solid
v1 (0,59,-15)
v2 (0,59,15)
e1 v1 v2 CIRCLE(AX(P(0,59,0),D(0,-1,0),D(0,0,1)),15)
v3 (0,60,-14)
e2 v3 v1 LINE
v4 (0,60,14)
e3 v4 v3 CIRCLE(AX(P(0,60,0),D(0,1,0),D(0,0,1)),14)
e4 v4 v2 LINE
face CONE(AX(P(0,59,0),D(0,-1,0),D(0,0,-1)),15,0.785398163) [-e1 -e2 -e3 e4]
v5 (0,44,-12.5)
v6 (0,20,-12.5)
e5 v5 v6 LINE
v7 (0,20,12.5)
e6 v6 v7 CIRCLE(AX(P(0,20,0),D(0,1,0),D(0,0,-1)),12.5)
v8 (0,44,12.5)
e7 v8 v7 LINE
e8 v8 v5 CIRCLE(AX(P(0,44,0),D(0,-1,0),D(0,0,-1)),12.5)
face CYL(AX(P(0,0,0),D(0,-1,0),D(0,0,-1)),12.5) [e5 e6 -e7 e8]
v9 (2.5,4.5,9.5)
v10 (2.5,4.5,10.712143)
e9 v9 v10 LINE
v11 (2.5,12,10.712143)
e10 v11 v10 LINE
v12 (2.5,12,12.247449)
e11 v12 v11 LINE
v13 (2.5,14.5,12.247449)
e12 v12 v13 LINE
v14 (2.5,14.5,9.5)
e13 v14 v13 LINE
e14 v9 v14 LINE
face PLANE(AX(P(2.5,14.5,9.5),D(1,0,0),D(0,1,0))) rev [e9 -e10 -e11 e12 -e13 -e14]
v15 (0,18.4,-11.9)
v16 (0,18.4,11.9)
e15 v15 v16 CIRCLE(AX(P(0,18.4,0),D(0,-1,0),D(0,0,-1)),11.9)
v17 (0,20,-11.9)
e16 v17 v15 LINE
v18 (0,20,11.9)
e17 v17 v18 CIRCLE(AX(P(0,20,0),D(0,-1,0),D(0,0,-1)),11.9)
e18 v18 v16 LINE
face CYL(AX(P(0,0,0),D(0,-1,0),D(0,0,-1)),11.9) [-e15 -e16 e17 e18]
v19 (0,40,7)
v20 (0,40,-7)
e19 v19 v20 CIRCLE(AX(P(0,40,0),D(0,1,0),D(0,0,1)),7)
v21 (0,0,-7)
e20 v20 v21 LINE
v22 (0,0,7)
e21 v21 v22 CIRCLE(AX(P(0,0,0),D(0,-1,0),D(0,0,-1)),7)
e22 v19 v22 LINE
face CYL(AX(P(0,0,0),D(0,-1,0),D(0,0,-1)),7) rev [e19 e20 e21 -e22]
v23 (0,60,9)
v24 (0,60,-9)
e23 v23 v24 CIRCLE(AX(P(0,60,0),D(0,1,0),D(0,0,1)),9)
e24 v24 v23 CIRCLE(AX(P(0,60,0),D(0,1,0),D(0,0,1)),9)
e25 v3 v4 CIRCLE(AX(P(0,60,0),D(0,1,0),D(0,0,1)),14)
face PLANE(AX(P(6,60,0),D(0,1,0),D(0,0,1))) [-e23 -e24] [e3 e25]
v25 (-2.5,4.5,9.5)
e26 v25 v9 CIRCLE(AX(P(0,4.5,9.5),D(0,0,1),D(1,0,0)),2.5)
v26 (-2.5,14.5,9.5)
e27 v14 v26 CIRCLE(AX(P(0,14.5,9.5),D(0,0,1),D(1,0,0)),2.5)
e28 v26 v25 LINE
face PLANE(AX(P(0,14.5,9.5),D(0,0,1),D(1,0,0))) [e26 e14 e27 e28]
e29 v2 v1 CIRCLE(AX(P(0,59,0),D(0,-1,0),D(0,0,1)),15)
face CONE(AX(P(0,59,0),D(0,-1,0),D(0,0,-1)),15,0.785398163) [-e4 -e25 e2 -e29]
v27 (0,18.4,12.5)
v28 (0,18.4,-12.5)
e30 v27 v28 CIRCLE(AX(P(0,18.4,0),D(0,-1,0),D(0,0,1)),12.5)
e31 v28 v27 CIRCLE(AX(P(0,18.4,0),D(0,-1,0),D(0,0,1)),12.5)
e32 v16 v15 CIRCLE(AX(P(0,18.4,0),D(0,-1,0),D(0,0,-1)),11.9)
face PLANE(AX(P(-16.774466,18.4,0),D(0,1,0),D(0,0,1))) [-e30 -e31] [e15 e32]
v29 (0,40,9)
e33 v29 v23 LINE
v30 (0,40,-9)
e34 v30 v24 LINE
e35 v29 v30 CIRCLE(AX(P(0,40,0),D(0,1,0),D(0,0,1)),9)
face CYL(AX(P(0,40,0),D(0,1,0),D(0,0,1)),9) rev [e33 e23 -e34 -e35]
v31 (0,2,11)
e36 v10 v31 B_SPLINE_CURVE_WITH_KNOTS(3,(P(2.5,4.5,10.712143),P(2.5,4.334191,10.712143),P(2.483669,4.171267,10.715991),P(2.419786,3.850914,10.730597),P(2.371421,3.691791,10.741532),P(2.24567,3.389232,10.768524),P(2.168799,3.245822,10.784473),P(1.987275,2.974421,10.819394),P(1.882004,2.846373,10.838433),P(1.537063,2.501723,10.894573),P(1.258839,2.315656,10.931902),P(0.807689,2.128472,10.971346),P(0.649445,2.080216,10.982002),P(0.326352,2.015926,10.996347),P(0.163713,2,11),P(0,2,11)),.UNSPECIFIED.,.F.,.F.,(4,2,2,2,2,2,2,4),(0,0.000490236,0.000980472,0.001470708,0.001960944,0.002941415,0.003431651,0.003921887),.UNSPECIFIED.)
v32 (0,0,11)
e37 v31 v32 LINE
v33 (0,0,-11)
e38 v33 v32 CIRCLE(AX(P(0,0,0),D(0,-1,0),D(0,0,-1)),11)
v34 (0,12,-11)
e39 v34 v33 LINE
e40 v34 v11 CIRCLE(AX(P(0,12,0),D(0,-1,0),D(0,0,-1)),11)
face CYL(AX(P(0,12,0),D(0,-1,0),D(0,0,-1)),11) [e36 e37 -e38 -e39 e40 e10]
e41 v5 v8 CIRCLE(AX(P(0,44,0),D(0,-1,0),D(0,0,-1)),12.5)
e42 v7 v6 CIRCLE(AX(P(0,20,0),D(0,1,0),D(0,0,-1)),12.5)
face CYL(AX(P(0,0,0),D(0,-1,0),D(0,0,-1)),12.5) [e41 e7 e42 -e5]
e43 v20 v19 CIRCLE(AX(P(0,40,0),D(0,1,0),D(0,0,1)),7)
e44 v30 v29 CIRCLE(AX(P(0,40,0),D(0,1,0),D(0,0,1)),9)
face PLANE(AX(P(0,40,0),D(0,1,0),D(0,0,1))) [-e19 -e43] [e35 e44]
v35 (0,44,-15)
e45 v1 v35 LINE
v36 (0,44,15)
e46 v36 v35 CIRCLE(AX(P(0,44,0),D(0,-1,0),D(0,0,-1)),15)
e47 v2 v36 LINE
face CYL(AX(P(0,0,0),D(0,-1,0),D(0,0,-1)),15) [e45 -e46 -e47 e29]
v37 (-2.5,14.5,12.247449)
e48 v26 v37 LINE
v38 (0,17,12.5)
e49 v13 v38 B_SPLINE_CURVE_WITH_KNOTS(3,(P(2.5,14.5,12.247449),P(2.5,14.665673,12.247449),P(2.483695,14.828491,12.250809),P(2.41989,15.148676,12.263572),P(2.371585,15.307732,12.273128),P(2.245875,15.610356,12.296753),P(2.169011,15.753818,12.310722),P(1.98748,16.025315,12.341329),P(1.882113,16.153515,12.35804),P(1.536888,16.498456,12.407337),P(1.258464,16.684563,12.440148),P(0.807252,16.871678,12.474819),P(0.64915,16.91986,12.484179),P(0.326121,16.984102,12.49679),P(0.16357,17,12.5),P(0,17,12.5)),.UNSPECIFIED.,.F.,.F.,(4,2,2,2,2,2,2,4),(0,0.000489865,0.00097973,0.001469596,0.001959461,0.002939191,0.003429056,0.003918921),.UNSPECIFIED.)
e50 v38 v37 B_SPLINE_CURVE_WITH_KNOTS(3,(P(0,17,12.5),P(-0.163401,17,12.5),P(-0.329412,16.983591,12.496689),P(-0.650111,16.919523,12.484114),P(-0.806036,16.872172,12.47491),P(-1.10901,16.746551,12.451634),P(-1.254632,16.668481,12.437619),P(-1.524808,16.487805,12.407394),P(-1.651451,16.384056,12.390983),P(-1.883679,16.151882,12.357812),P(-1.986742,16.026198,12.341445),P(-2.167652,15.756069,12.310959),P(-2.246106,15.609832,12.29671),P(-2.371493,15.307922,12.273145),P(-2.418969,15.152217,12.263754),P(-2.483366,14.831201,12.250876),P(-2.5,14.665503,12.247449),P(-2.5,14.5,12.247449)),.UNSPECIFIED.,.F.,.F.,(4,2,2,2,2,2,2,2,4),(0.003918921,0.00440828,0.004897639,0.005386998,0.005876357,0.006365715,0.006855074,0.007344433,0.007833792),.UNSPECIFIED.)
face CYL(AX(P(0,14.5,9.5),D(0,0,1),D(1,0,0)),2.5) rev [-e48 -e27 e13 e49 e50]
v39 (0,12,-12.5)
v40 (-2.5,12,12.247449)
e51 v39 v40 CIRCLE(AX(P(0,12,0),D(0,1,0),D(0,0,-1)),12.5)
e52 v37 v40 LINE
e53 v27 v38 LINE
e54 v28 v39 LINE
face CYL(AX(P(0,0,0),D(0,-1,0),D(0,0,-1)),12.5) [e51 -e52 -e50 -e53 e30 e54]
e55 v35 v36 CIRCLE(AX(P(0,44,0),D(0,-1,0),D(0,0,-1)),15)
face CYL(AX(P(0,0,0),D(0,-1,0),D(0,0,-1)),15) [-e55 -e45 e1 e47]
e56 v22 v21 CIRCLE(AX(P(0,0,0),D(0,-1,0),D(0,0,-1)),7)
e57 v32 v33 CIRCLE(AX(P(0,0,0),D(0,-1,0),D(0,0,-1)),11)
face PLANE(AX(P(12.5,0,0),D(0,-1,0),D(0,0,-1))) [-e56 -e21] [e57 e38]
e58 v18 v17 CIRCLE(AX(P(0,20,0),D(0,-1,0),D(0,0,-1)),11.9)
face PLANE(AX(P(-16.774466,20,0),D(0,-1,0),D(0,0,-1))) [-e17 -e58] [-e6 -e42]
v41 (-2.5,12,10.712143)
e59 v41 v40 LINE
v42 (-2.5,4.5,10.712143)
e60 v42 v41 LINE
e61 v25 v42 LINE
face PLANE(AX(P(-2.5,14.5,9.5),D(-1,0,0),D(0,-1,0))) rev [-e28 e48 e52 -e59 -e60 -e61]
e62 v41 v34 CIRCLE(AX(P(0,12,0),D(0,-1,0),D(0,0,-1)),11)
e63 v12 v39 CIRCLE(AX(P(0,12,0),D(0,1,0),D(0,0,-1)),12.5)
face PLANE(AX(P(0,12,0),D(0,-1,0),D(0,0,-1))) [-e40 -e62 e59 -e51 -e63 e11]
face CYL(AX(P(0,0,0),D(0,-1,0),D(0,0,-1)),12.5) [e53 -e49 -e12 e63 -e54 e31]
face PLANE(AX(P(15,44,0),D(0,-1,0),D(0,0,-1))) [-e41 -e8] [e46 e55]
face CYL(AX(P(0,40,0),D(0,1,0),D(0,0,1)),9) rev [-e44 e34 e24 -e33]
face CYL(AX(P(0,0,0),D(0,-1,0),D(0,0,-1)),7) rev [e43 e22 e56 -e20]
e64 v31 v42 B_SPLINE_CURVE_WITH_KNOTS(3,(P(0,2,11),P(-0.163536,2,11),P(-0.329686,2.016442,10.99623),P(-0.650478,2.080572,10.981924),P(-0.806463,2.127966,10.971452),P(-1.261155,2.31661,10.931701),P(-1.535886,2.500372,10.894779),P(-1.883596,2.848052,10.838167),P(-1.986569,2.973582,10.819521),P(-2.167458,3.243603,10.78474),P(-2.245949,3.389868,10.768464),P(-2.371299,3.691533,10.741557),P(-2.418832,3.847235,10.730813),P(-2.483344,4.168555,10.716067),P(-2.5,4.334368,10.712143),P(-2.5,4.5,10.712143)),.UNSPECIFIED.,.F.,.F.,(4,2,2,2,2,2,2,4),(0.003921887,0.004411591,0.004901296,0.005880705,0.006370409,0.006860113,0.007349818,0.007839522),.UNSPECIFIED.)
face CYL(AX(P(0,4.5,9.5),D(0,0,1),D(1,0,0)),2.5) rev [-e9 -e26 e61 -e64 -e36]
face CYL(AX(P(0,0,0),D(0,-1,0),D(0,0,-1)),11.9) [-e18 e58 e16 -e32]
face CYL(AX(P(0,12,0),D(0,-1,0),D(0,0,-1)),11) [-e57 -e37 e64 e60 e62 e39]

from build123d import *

# Parameters (mm, degrees)
SKETCH2_W          = 4.874466188
SKETCH2_H          = 1.6
SKETCH3_R          = 9
CUT_EXTRUDE1_DEPTH = 20
M16_TAPPED_HOLE2_D = 14
CHAMFER1_SIZE      = 1
CUT_EXTRUDE2_START = 12.5
CUT_EXTRUDE2_DEPTH = 3
SKETCH10_R         = 15
SKETCH10_R_2       = 11
CUT_EXTRUDE3_DEPTH = 12


with BuildPart() as part:
    # Sketch1 → Revolve1 (revolve)
    with BuildSketch(Plane.XY, mode=Mode.PRIVATE) as revolve1_sk:
        Polygon((6, 60), (15, 60), (15, 44), (12.5, 44), (12.5, 0), (6, 0), align=None)
    revolve(revolve1_sk.sketch.rotate(Axis((0, 0, 0), (0, 1, 0)), 90), axis=Axis((0, 0, 0), (0, 1, 0)))

    # Sketch2 → Cut-Revolve1 (revolve, cut)
    with BuildSketch(Plane.XY, mode=Mode.PRIVATE) as cut_revolve1_sk:
        with Locations((-14.337233094, 19.2)):
            Rectangle(SKETCH2_W, SKETCH2_H)
    revolve(cut_revolve1_sk.sketch.rotate(Axis((0, 0, 0), (0, 1, 0)), 270), axis=Axis((0, 0, 0), (0, 1, 0)), mode=Mode.SUBTRACT)

    # Sketch3 → Cut-Extrude1 (cut)
    with BuildSketch(Plane(origin=(0, 60, 0), x_dir=(1, 0, 0), z_dir=(0, 1, 0))):
        with Locations(Location((0, 0, 0), (0, 0, 270))):
            Circle(SKETCH3_R)
    extrude(amount=-CUT_EXTRUDE1_DEPTH, mode=Mode.SUBTRACT)

    # M16 Tapped Hole2 (through all)
    with Locations(Plane(origin=(0, 0, 0), x_dir=(-1, 0, 0), z_dir=(0, -1, 0))):
        with Locations((0, 0)):
            Hole(M16_TAPPED_HOLE2_D / 2)

    # Chamfer1
    chamfer1_edges = [part.edges().sort_by_distance(p)[0] for p in [
        (0, 0, 12.5),
        (0, 60, 15),
    ]]
    chamfer(chamfer1_edges, length=CHAMFER1_SIZE)

    # Sketch8 → Cut-Extrude2 (cut)
    with BuildSketch(Plane.XY.offset(CUT_EXTRUDE2_START)):
        with BuildLine():
            Line((2.5, 14.5), (2.5, 4.5))
            ThreePointArc((2.5, 4.5), (0, 2), (-2.5, 4.5))
            Line((-2.5, 4.5), (-2.5, 14.5))
            ThreePointArc((-2.5, 14.5), (0, 17), (2.5, 14.5))
        make_face()
    extrude(amount=-CUT_EXTRUDE2_DEPTH, mode=Mode.SUBTRACT)

    # Sketch10 → Cut-Extrude3 (cut)
    with BuildSketch(Plane.XZ):
        with Locations(Location((0, 0, 0), (0, 0, 270))):
            Circle(SKETCH10_R)
        with Locations(Location((0, 0, 0), (0, 0, 270))):
            Circle(SKETCH10_R_2, mode=Mode.SUBTRACT)
    extrude(amount=-CUT_EXTRUDE3_DEPTH, mode=Mode.SUBTRACT)


solid = part.part
